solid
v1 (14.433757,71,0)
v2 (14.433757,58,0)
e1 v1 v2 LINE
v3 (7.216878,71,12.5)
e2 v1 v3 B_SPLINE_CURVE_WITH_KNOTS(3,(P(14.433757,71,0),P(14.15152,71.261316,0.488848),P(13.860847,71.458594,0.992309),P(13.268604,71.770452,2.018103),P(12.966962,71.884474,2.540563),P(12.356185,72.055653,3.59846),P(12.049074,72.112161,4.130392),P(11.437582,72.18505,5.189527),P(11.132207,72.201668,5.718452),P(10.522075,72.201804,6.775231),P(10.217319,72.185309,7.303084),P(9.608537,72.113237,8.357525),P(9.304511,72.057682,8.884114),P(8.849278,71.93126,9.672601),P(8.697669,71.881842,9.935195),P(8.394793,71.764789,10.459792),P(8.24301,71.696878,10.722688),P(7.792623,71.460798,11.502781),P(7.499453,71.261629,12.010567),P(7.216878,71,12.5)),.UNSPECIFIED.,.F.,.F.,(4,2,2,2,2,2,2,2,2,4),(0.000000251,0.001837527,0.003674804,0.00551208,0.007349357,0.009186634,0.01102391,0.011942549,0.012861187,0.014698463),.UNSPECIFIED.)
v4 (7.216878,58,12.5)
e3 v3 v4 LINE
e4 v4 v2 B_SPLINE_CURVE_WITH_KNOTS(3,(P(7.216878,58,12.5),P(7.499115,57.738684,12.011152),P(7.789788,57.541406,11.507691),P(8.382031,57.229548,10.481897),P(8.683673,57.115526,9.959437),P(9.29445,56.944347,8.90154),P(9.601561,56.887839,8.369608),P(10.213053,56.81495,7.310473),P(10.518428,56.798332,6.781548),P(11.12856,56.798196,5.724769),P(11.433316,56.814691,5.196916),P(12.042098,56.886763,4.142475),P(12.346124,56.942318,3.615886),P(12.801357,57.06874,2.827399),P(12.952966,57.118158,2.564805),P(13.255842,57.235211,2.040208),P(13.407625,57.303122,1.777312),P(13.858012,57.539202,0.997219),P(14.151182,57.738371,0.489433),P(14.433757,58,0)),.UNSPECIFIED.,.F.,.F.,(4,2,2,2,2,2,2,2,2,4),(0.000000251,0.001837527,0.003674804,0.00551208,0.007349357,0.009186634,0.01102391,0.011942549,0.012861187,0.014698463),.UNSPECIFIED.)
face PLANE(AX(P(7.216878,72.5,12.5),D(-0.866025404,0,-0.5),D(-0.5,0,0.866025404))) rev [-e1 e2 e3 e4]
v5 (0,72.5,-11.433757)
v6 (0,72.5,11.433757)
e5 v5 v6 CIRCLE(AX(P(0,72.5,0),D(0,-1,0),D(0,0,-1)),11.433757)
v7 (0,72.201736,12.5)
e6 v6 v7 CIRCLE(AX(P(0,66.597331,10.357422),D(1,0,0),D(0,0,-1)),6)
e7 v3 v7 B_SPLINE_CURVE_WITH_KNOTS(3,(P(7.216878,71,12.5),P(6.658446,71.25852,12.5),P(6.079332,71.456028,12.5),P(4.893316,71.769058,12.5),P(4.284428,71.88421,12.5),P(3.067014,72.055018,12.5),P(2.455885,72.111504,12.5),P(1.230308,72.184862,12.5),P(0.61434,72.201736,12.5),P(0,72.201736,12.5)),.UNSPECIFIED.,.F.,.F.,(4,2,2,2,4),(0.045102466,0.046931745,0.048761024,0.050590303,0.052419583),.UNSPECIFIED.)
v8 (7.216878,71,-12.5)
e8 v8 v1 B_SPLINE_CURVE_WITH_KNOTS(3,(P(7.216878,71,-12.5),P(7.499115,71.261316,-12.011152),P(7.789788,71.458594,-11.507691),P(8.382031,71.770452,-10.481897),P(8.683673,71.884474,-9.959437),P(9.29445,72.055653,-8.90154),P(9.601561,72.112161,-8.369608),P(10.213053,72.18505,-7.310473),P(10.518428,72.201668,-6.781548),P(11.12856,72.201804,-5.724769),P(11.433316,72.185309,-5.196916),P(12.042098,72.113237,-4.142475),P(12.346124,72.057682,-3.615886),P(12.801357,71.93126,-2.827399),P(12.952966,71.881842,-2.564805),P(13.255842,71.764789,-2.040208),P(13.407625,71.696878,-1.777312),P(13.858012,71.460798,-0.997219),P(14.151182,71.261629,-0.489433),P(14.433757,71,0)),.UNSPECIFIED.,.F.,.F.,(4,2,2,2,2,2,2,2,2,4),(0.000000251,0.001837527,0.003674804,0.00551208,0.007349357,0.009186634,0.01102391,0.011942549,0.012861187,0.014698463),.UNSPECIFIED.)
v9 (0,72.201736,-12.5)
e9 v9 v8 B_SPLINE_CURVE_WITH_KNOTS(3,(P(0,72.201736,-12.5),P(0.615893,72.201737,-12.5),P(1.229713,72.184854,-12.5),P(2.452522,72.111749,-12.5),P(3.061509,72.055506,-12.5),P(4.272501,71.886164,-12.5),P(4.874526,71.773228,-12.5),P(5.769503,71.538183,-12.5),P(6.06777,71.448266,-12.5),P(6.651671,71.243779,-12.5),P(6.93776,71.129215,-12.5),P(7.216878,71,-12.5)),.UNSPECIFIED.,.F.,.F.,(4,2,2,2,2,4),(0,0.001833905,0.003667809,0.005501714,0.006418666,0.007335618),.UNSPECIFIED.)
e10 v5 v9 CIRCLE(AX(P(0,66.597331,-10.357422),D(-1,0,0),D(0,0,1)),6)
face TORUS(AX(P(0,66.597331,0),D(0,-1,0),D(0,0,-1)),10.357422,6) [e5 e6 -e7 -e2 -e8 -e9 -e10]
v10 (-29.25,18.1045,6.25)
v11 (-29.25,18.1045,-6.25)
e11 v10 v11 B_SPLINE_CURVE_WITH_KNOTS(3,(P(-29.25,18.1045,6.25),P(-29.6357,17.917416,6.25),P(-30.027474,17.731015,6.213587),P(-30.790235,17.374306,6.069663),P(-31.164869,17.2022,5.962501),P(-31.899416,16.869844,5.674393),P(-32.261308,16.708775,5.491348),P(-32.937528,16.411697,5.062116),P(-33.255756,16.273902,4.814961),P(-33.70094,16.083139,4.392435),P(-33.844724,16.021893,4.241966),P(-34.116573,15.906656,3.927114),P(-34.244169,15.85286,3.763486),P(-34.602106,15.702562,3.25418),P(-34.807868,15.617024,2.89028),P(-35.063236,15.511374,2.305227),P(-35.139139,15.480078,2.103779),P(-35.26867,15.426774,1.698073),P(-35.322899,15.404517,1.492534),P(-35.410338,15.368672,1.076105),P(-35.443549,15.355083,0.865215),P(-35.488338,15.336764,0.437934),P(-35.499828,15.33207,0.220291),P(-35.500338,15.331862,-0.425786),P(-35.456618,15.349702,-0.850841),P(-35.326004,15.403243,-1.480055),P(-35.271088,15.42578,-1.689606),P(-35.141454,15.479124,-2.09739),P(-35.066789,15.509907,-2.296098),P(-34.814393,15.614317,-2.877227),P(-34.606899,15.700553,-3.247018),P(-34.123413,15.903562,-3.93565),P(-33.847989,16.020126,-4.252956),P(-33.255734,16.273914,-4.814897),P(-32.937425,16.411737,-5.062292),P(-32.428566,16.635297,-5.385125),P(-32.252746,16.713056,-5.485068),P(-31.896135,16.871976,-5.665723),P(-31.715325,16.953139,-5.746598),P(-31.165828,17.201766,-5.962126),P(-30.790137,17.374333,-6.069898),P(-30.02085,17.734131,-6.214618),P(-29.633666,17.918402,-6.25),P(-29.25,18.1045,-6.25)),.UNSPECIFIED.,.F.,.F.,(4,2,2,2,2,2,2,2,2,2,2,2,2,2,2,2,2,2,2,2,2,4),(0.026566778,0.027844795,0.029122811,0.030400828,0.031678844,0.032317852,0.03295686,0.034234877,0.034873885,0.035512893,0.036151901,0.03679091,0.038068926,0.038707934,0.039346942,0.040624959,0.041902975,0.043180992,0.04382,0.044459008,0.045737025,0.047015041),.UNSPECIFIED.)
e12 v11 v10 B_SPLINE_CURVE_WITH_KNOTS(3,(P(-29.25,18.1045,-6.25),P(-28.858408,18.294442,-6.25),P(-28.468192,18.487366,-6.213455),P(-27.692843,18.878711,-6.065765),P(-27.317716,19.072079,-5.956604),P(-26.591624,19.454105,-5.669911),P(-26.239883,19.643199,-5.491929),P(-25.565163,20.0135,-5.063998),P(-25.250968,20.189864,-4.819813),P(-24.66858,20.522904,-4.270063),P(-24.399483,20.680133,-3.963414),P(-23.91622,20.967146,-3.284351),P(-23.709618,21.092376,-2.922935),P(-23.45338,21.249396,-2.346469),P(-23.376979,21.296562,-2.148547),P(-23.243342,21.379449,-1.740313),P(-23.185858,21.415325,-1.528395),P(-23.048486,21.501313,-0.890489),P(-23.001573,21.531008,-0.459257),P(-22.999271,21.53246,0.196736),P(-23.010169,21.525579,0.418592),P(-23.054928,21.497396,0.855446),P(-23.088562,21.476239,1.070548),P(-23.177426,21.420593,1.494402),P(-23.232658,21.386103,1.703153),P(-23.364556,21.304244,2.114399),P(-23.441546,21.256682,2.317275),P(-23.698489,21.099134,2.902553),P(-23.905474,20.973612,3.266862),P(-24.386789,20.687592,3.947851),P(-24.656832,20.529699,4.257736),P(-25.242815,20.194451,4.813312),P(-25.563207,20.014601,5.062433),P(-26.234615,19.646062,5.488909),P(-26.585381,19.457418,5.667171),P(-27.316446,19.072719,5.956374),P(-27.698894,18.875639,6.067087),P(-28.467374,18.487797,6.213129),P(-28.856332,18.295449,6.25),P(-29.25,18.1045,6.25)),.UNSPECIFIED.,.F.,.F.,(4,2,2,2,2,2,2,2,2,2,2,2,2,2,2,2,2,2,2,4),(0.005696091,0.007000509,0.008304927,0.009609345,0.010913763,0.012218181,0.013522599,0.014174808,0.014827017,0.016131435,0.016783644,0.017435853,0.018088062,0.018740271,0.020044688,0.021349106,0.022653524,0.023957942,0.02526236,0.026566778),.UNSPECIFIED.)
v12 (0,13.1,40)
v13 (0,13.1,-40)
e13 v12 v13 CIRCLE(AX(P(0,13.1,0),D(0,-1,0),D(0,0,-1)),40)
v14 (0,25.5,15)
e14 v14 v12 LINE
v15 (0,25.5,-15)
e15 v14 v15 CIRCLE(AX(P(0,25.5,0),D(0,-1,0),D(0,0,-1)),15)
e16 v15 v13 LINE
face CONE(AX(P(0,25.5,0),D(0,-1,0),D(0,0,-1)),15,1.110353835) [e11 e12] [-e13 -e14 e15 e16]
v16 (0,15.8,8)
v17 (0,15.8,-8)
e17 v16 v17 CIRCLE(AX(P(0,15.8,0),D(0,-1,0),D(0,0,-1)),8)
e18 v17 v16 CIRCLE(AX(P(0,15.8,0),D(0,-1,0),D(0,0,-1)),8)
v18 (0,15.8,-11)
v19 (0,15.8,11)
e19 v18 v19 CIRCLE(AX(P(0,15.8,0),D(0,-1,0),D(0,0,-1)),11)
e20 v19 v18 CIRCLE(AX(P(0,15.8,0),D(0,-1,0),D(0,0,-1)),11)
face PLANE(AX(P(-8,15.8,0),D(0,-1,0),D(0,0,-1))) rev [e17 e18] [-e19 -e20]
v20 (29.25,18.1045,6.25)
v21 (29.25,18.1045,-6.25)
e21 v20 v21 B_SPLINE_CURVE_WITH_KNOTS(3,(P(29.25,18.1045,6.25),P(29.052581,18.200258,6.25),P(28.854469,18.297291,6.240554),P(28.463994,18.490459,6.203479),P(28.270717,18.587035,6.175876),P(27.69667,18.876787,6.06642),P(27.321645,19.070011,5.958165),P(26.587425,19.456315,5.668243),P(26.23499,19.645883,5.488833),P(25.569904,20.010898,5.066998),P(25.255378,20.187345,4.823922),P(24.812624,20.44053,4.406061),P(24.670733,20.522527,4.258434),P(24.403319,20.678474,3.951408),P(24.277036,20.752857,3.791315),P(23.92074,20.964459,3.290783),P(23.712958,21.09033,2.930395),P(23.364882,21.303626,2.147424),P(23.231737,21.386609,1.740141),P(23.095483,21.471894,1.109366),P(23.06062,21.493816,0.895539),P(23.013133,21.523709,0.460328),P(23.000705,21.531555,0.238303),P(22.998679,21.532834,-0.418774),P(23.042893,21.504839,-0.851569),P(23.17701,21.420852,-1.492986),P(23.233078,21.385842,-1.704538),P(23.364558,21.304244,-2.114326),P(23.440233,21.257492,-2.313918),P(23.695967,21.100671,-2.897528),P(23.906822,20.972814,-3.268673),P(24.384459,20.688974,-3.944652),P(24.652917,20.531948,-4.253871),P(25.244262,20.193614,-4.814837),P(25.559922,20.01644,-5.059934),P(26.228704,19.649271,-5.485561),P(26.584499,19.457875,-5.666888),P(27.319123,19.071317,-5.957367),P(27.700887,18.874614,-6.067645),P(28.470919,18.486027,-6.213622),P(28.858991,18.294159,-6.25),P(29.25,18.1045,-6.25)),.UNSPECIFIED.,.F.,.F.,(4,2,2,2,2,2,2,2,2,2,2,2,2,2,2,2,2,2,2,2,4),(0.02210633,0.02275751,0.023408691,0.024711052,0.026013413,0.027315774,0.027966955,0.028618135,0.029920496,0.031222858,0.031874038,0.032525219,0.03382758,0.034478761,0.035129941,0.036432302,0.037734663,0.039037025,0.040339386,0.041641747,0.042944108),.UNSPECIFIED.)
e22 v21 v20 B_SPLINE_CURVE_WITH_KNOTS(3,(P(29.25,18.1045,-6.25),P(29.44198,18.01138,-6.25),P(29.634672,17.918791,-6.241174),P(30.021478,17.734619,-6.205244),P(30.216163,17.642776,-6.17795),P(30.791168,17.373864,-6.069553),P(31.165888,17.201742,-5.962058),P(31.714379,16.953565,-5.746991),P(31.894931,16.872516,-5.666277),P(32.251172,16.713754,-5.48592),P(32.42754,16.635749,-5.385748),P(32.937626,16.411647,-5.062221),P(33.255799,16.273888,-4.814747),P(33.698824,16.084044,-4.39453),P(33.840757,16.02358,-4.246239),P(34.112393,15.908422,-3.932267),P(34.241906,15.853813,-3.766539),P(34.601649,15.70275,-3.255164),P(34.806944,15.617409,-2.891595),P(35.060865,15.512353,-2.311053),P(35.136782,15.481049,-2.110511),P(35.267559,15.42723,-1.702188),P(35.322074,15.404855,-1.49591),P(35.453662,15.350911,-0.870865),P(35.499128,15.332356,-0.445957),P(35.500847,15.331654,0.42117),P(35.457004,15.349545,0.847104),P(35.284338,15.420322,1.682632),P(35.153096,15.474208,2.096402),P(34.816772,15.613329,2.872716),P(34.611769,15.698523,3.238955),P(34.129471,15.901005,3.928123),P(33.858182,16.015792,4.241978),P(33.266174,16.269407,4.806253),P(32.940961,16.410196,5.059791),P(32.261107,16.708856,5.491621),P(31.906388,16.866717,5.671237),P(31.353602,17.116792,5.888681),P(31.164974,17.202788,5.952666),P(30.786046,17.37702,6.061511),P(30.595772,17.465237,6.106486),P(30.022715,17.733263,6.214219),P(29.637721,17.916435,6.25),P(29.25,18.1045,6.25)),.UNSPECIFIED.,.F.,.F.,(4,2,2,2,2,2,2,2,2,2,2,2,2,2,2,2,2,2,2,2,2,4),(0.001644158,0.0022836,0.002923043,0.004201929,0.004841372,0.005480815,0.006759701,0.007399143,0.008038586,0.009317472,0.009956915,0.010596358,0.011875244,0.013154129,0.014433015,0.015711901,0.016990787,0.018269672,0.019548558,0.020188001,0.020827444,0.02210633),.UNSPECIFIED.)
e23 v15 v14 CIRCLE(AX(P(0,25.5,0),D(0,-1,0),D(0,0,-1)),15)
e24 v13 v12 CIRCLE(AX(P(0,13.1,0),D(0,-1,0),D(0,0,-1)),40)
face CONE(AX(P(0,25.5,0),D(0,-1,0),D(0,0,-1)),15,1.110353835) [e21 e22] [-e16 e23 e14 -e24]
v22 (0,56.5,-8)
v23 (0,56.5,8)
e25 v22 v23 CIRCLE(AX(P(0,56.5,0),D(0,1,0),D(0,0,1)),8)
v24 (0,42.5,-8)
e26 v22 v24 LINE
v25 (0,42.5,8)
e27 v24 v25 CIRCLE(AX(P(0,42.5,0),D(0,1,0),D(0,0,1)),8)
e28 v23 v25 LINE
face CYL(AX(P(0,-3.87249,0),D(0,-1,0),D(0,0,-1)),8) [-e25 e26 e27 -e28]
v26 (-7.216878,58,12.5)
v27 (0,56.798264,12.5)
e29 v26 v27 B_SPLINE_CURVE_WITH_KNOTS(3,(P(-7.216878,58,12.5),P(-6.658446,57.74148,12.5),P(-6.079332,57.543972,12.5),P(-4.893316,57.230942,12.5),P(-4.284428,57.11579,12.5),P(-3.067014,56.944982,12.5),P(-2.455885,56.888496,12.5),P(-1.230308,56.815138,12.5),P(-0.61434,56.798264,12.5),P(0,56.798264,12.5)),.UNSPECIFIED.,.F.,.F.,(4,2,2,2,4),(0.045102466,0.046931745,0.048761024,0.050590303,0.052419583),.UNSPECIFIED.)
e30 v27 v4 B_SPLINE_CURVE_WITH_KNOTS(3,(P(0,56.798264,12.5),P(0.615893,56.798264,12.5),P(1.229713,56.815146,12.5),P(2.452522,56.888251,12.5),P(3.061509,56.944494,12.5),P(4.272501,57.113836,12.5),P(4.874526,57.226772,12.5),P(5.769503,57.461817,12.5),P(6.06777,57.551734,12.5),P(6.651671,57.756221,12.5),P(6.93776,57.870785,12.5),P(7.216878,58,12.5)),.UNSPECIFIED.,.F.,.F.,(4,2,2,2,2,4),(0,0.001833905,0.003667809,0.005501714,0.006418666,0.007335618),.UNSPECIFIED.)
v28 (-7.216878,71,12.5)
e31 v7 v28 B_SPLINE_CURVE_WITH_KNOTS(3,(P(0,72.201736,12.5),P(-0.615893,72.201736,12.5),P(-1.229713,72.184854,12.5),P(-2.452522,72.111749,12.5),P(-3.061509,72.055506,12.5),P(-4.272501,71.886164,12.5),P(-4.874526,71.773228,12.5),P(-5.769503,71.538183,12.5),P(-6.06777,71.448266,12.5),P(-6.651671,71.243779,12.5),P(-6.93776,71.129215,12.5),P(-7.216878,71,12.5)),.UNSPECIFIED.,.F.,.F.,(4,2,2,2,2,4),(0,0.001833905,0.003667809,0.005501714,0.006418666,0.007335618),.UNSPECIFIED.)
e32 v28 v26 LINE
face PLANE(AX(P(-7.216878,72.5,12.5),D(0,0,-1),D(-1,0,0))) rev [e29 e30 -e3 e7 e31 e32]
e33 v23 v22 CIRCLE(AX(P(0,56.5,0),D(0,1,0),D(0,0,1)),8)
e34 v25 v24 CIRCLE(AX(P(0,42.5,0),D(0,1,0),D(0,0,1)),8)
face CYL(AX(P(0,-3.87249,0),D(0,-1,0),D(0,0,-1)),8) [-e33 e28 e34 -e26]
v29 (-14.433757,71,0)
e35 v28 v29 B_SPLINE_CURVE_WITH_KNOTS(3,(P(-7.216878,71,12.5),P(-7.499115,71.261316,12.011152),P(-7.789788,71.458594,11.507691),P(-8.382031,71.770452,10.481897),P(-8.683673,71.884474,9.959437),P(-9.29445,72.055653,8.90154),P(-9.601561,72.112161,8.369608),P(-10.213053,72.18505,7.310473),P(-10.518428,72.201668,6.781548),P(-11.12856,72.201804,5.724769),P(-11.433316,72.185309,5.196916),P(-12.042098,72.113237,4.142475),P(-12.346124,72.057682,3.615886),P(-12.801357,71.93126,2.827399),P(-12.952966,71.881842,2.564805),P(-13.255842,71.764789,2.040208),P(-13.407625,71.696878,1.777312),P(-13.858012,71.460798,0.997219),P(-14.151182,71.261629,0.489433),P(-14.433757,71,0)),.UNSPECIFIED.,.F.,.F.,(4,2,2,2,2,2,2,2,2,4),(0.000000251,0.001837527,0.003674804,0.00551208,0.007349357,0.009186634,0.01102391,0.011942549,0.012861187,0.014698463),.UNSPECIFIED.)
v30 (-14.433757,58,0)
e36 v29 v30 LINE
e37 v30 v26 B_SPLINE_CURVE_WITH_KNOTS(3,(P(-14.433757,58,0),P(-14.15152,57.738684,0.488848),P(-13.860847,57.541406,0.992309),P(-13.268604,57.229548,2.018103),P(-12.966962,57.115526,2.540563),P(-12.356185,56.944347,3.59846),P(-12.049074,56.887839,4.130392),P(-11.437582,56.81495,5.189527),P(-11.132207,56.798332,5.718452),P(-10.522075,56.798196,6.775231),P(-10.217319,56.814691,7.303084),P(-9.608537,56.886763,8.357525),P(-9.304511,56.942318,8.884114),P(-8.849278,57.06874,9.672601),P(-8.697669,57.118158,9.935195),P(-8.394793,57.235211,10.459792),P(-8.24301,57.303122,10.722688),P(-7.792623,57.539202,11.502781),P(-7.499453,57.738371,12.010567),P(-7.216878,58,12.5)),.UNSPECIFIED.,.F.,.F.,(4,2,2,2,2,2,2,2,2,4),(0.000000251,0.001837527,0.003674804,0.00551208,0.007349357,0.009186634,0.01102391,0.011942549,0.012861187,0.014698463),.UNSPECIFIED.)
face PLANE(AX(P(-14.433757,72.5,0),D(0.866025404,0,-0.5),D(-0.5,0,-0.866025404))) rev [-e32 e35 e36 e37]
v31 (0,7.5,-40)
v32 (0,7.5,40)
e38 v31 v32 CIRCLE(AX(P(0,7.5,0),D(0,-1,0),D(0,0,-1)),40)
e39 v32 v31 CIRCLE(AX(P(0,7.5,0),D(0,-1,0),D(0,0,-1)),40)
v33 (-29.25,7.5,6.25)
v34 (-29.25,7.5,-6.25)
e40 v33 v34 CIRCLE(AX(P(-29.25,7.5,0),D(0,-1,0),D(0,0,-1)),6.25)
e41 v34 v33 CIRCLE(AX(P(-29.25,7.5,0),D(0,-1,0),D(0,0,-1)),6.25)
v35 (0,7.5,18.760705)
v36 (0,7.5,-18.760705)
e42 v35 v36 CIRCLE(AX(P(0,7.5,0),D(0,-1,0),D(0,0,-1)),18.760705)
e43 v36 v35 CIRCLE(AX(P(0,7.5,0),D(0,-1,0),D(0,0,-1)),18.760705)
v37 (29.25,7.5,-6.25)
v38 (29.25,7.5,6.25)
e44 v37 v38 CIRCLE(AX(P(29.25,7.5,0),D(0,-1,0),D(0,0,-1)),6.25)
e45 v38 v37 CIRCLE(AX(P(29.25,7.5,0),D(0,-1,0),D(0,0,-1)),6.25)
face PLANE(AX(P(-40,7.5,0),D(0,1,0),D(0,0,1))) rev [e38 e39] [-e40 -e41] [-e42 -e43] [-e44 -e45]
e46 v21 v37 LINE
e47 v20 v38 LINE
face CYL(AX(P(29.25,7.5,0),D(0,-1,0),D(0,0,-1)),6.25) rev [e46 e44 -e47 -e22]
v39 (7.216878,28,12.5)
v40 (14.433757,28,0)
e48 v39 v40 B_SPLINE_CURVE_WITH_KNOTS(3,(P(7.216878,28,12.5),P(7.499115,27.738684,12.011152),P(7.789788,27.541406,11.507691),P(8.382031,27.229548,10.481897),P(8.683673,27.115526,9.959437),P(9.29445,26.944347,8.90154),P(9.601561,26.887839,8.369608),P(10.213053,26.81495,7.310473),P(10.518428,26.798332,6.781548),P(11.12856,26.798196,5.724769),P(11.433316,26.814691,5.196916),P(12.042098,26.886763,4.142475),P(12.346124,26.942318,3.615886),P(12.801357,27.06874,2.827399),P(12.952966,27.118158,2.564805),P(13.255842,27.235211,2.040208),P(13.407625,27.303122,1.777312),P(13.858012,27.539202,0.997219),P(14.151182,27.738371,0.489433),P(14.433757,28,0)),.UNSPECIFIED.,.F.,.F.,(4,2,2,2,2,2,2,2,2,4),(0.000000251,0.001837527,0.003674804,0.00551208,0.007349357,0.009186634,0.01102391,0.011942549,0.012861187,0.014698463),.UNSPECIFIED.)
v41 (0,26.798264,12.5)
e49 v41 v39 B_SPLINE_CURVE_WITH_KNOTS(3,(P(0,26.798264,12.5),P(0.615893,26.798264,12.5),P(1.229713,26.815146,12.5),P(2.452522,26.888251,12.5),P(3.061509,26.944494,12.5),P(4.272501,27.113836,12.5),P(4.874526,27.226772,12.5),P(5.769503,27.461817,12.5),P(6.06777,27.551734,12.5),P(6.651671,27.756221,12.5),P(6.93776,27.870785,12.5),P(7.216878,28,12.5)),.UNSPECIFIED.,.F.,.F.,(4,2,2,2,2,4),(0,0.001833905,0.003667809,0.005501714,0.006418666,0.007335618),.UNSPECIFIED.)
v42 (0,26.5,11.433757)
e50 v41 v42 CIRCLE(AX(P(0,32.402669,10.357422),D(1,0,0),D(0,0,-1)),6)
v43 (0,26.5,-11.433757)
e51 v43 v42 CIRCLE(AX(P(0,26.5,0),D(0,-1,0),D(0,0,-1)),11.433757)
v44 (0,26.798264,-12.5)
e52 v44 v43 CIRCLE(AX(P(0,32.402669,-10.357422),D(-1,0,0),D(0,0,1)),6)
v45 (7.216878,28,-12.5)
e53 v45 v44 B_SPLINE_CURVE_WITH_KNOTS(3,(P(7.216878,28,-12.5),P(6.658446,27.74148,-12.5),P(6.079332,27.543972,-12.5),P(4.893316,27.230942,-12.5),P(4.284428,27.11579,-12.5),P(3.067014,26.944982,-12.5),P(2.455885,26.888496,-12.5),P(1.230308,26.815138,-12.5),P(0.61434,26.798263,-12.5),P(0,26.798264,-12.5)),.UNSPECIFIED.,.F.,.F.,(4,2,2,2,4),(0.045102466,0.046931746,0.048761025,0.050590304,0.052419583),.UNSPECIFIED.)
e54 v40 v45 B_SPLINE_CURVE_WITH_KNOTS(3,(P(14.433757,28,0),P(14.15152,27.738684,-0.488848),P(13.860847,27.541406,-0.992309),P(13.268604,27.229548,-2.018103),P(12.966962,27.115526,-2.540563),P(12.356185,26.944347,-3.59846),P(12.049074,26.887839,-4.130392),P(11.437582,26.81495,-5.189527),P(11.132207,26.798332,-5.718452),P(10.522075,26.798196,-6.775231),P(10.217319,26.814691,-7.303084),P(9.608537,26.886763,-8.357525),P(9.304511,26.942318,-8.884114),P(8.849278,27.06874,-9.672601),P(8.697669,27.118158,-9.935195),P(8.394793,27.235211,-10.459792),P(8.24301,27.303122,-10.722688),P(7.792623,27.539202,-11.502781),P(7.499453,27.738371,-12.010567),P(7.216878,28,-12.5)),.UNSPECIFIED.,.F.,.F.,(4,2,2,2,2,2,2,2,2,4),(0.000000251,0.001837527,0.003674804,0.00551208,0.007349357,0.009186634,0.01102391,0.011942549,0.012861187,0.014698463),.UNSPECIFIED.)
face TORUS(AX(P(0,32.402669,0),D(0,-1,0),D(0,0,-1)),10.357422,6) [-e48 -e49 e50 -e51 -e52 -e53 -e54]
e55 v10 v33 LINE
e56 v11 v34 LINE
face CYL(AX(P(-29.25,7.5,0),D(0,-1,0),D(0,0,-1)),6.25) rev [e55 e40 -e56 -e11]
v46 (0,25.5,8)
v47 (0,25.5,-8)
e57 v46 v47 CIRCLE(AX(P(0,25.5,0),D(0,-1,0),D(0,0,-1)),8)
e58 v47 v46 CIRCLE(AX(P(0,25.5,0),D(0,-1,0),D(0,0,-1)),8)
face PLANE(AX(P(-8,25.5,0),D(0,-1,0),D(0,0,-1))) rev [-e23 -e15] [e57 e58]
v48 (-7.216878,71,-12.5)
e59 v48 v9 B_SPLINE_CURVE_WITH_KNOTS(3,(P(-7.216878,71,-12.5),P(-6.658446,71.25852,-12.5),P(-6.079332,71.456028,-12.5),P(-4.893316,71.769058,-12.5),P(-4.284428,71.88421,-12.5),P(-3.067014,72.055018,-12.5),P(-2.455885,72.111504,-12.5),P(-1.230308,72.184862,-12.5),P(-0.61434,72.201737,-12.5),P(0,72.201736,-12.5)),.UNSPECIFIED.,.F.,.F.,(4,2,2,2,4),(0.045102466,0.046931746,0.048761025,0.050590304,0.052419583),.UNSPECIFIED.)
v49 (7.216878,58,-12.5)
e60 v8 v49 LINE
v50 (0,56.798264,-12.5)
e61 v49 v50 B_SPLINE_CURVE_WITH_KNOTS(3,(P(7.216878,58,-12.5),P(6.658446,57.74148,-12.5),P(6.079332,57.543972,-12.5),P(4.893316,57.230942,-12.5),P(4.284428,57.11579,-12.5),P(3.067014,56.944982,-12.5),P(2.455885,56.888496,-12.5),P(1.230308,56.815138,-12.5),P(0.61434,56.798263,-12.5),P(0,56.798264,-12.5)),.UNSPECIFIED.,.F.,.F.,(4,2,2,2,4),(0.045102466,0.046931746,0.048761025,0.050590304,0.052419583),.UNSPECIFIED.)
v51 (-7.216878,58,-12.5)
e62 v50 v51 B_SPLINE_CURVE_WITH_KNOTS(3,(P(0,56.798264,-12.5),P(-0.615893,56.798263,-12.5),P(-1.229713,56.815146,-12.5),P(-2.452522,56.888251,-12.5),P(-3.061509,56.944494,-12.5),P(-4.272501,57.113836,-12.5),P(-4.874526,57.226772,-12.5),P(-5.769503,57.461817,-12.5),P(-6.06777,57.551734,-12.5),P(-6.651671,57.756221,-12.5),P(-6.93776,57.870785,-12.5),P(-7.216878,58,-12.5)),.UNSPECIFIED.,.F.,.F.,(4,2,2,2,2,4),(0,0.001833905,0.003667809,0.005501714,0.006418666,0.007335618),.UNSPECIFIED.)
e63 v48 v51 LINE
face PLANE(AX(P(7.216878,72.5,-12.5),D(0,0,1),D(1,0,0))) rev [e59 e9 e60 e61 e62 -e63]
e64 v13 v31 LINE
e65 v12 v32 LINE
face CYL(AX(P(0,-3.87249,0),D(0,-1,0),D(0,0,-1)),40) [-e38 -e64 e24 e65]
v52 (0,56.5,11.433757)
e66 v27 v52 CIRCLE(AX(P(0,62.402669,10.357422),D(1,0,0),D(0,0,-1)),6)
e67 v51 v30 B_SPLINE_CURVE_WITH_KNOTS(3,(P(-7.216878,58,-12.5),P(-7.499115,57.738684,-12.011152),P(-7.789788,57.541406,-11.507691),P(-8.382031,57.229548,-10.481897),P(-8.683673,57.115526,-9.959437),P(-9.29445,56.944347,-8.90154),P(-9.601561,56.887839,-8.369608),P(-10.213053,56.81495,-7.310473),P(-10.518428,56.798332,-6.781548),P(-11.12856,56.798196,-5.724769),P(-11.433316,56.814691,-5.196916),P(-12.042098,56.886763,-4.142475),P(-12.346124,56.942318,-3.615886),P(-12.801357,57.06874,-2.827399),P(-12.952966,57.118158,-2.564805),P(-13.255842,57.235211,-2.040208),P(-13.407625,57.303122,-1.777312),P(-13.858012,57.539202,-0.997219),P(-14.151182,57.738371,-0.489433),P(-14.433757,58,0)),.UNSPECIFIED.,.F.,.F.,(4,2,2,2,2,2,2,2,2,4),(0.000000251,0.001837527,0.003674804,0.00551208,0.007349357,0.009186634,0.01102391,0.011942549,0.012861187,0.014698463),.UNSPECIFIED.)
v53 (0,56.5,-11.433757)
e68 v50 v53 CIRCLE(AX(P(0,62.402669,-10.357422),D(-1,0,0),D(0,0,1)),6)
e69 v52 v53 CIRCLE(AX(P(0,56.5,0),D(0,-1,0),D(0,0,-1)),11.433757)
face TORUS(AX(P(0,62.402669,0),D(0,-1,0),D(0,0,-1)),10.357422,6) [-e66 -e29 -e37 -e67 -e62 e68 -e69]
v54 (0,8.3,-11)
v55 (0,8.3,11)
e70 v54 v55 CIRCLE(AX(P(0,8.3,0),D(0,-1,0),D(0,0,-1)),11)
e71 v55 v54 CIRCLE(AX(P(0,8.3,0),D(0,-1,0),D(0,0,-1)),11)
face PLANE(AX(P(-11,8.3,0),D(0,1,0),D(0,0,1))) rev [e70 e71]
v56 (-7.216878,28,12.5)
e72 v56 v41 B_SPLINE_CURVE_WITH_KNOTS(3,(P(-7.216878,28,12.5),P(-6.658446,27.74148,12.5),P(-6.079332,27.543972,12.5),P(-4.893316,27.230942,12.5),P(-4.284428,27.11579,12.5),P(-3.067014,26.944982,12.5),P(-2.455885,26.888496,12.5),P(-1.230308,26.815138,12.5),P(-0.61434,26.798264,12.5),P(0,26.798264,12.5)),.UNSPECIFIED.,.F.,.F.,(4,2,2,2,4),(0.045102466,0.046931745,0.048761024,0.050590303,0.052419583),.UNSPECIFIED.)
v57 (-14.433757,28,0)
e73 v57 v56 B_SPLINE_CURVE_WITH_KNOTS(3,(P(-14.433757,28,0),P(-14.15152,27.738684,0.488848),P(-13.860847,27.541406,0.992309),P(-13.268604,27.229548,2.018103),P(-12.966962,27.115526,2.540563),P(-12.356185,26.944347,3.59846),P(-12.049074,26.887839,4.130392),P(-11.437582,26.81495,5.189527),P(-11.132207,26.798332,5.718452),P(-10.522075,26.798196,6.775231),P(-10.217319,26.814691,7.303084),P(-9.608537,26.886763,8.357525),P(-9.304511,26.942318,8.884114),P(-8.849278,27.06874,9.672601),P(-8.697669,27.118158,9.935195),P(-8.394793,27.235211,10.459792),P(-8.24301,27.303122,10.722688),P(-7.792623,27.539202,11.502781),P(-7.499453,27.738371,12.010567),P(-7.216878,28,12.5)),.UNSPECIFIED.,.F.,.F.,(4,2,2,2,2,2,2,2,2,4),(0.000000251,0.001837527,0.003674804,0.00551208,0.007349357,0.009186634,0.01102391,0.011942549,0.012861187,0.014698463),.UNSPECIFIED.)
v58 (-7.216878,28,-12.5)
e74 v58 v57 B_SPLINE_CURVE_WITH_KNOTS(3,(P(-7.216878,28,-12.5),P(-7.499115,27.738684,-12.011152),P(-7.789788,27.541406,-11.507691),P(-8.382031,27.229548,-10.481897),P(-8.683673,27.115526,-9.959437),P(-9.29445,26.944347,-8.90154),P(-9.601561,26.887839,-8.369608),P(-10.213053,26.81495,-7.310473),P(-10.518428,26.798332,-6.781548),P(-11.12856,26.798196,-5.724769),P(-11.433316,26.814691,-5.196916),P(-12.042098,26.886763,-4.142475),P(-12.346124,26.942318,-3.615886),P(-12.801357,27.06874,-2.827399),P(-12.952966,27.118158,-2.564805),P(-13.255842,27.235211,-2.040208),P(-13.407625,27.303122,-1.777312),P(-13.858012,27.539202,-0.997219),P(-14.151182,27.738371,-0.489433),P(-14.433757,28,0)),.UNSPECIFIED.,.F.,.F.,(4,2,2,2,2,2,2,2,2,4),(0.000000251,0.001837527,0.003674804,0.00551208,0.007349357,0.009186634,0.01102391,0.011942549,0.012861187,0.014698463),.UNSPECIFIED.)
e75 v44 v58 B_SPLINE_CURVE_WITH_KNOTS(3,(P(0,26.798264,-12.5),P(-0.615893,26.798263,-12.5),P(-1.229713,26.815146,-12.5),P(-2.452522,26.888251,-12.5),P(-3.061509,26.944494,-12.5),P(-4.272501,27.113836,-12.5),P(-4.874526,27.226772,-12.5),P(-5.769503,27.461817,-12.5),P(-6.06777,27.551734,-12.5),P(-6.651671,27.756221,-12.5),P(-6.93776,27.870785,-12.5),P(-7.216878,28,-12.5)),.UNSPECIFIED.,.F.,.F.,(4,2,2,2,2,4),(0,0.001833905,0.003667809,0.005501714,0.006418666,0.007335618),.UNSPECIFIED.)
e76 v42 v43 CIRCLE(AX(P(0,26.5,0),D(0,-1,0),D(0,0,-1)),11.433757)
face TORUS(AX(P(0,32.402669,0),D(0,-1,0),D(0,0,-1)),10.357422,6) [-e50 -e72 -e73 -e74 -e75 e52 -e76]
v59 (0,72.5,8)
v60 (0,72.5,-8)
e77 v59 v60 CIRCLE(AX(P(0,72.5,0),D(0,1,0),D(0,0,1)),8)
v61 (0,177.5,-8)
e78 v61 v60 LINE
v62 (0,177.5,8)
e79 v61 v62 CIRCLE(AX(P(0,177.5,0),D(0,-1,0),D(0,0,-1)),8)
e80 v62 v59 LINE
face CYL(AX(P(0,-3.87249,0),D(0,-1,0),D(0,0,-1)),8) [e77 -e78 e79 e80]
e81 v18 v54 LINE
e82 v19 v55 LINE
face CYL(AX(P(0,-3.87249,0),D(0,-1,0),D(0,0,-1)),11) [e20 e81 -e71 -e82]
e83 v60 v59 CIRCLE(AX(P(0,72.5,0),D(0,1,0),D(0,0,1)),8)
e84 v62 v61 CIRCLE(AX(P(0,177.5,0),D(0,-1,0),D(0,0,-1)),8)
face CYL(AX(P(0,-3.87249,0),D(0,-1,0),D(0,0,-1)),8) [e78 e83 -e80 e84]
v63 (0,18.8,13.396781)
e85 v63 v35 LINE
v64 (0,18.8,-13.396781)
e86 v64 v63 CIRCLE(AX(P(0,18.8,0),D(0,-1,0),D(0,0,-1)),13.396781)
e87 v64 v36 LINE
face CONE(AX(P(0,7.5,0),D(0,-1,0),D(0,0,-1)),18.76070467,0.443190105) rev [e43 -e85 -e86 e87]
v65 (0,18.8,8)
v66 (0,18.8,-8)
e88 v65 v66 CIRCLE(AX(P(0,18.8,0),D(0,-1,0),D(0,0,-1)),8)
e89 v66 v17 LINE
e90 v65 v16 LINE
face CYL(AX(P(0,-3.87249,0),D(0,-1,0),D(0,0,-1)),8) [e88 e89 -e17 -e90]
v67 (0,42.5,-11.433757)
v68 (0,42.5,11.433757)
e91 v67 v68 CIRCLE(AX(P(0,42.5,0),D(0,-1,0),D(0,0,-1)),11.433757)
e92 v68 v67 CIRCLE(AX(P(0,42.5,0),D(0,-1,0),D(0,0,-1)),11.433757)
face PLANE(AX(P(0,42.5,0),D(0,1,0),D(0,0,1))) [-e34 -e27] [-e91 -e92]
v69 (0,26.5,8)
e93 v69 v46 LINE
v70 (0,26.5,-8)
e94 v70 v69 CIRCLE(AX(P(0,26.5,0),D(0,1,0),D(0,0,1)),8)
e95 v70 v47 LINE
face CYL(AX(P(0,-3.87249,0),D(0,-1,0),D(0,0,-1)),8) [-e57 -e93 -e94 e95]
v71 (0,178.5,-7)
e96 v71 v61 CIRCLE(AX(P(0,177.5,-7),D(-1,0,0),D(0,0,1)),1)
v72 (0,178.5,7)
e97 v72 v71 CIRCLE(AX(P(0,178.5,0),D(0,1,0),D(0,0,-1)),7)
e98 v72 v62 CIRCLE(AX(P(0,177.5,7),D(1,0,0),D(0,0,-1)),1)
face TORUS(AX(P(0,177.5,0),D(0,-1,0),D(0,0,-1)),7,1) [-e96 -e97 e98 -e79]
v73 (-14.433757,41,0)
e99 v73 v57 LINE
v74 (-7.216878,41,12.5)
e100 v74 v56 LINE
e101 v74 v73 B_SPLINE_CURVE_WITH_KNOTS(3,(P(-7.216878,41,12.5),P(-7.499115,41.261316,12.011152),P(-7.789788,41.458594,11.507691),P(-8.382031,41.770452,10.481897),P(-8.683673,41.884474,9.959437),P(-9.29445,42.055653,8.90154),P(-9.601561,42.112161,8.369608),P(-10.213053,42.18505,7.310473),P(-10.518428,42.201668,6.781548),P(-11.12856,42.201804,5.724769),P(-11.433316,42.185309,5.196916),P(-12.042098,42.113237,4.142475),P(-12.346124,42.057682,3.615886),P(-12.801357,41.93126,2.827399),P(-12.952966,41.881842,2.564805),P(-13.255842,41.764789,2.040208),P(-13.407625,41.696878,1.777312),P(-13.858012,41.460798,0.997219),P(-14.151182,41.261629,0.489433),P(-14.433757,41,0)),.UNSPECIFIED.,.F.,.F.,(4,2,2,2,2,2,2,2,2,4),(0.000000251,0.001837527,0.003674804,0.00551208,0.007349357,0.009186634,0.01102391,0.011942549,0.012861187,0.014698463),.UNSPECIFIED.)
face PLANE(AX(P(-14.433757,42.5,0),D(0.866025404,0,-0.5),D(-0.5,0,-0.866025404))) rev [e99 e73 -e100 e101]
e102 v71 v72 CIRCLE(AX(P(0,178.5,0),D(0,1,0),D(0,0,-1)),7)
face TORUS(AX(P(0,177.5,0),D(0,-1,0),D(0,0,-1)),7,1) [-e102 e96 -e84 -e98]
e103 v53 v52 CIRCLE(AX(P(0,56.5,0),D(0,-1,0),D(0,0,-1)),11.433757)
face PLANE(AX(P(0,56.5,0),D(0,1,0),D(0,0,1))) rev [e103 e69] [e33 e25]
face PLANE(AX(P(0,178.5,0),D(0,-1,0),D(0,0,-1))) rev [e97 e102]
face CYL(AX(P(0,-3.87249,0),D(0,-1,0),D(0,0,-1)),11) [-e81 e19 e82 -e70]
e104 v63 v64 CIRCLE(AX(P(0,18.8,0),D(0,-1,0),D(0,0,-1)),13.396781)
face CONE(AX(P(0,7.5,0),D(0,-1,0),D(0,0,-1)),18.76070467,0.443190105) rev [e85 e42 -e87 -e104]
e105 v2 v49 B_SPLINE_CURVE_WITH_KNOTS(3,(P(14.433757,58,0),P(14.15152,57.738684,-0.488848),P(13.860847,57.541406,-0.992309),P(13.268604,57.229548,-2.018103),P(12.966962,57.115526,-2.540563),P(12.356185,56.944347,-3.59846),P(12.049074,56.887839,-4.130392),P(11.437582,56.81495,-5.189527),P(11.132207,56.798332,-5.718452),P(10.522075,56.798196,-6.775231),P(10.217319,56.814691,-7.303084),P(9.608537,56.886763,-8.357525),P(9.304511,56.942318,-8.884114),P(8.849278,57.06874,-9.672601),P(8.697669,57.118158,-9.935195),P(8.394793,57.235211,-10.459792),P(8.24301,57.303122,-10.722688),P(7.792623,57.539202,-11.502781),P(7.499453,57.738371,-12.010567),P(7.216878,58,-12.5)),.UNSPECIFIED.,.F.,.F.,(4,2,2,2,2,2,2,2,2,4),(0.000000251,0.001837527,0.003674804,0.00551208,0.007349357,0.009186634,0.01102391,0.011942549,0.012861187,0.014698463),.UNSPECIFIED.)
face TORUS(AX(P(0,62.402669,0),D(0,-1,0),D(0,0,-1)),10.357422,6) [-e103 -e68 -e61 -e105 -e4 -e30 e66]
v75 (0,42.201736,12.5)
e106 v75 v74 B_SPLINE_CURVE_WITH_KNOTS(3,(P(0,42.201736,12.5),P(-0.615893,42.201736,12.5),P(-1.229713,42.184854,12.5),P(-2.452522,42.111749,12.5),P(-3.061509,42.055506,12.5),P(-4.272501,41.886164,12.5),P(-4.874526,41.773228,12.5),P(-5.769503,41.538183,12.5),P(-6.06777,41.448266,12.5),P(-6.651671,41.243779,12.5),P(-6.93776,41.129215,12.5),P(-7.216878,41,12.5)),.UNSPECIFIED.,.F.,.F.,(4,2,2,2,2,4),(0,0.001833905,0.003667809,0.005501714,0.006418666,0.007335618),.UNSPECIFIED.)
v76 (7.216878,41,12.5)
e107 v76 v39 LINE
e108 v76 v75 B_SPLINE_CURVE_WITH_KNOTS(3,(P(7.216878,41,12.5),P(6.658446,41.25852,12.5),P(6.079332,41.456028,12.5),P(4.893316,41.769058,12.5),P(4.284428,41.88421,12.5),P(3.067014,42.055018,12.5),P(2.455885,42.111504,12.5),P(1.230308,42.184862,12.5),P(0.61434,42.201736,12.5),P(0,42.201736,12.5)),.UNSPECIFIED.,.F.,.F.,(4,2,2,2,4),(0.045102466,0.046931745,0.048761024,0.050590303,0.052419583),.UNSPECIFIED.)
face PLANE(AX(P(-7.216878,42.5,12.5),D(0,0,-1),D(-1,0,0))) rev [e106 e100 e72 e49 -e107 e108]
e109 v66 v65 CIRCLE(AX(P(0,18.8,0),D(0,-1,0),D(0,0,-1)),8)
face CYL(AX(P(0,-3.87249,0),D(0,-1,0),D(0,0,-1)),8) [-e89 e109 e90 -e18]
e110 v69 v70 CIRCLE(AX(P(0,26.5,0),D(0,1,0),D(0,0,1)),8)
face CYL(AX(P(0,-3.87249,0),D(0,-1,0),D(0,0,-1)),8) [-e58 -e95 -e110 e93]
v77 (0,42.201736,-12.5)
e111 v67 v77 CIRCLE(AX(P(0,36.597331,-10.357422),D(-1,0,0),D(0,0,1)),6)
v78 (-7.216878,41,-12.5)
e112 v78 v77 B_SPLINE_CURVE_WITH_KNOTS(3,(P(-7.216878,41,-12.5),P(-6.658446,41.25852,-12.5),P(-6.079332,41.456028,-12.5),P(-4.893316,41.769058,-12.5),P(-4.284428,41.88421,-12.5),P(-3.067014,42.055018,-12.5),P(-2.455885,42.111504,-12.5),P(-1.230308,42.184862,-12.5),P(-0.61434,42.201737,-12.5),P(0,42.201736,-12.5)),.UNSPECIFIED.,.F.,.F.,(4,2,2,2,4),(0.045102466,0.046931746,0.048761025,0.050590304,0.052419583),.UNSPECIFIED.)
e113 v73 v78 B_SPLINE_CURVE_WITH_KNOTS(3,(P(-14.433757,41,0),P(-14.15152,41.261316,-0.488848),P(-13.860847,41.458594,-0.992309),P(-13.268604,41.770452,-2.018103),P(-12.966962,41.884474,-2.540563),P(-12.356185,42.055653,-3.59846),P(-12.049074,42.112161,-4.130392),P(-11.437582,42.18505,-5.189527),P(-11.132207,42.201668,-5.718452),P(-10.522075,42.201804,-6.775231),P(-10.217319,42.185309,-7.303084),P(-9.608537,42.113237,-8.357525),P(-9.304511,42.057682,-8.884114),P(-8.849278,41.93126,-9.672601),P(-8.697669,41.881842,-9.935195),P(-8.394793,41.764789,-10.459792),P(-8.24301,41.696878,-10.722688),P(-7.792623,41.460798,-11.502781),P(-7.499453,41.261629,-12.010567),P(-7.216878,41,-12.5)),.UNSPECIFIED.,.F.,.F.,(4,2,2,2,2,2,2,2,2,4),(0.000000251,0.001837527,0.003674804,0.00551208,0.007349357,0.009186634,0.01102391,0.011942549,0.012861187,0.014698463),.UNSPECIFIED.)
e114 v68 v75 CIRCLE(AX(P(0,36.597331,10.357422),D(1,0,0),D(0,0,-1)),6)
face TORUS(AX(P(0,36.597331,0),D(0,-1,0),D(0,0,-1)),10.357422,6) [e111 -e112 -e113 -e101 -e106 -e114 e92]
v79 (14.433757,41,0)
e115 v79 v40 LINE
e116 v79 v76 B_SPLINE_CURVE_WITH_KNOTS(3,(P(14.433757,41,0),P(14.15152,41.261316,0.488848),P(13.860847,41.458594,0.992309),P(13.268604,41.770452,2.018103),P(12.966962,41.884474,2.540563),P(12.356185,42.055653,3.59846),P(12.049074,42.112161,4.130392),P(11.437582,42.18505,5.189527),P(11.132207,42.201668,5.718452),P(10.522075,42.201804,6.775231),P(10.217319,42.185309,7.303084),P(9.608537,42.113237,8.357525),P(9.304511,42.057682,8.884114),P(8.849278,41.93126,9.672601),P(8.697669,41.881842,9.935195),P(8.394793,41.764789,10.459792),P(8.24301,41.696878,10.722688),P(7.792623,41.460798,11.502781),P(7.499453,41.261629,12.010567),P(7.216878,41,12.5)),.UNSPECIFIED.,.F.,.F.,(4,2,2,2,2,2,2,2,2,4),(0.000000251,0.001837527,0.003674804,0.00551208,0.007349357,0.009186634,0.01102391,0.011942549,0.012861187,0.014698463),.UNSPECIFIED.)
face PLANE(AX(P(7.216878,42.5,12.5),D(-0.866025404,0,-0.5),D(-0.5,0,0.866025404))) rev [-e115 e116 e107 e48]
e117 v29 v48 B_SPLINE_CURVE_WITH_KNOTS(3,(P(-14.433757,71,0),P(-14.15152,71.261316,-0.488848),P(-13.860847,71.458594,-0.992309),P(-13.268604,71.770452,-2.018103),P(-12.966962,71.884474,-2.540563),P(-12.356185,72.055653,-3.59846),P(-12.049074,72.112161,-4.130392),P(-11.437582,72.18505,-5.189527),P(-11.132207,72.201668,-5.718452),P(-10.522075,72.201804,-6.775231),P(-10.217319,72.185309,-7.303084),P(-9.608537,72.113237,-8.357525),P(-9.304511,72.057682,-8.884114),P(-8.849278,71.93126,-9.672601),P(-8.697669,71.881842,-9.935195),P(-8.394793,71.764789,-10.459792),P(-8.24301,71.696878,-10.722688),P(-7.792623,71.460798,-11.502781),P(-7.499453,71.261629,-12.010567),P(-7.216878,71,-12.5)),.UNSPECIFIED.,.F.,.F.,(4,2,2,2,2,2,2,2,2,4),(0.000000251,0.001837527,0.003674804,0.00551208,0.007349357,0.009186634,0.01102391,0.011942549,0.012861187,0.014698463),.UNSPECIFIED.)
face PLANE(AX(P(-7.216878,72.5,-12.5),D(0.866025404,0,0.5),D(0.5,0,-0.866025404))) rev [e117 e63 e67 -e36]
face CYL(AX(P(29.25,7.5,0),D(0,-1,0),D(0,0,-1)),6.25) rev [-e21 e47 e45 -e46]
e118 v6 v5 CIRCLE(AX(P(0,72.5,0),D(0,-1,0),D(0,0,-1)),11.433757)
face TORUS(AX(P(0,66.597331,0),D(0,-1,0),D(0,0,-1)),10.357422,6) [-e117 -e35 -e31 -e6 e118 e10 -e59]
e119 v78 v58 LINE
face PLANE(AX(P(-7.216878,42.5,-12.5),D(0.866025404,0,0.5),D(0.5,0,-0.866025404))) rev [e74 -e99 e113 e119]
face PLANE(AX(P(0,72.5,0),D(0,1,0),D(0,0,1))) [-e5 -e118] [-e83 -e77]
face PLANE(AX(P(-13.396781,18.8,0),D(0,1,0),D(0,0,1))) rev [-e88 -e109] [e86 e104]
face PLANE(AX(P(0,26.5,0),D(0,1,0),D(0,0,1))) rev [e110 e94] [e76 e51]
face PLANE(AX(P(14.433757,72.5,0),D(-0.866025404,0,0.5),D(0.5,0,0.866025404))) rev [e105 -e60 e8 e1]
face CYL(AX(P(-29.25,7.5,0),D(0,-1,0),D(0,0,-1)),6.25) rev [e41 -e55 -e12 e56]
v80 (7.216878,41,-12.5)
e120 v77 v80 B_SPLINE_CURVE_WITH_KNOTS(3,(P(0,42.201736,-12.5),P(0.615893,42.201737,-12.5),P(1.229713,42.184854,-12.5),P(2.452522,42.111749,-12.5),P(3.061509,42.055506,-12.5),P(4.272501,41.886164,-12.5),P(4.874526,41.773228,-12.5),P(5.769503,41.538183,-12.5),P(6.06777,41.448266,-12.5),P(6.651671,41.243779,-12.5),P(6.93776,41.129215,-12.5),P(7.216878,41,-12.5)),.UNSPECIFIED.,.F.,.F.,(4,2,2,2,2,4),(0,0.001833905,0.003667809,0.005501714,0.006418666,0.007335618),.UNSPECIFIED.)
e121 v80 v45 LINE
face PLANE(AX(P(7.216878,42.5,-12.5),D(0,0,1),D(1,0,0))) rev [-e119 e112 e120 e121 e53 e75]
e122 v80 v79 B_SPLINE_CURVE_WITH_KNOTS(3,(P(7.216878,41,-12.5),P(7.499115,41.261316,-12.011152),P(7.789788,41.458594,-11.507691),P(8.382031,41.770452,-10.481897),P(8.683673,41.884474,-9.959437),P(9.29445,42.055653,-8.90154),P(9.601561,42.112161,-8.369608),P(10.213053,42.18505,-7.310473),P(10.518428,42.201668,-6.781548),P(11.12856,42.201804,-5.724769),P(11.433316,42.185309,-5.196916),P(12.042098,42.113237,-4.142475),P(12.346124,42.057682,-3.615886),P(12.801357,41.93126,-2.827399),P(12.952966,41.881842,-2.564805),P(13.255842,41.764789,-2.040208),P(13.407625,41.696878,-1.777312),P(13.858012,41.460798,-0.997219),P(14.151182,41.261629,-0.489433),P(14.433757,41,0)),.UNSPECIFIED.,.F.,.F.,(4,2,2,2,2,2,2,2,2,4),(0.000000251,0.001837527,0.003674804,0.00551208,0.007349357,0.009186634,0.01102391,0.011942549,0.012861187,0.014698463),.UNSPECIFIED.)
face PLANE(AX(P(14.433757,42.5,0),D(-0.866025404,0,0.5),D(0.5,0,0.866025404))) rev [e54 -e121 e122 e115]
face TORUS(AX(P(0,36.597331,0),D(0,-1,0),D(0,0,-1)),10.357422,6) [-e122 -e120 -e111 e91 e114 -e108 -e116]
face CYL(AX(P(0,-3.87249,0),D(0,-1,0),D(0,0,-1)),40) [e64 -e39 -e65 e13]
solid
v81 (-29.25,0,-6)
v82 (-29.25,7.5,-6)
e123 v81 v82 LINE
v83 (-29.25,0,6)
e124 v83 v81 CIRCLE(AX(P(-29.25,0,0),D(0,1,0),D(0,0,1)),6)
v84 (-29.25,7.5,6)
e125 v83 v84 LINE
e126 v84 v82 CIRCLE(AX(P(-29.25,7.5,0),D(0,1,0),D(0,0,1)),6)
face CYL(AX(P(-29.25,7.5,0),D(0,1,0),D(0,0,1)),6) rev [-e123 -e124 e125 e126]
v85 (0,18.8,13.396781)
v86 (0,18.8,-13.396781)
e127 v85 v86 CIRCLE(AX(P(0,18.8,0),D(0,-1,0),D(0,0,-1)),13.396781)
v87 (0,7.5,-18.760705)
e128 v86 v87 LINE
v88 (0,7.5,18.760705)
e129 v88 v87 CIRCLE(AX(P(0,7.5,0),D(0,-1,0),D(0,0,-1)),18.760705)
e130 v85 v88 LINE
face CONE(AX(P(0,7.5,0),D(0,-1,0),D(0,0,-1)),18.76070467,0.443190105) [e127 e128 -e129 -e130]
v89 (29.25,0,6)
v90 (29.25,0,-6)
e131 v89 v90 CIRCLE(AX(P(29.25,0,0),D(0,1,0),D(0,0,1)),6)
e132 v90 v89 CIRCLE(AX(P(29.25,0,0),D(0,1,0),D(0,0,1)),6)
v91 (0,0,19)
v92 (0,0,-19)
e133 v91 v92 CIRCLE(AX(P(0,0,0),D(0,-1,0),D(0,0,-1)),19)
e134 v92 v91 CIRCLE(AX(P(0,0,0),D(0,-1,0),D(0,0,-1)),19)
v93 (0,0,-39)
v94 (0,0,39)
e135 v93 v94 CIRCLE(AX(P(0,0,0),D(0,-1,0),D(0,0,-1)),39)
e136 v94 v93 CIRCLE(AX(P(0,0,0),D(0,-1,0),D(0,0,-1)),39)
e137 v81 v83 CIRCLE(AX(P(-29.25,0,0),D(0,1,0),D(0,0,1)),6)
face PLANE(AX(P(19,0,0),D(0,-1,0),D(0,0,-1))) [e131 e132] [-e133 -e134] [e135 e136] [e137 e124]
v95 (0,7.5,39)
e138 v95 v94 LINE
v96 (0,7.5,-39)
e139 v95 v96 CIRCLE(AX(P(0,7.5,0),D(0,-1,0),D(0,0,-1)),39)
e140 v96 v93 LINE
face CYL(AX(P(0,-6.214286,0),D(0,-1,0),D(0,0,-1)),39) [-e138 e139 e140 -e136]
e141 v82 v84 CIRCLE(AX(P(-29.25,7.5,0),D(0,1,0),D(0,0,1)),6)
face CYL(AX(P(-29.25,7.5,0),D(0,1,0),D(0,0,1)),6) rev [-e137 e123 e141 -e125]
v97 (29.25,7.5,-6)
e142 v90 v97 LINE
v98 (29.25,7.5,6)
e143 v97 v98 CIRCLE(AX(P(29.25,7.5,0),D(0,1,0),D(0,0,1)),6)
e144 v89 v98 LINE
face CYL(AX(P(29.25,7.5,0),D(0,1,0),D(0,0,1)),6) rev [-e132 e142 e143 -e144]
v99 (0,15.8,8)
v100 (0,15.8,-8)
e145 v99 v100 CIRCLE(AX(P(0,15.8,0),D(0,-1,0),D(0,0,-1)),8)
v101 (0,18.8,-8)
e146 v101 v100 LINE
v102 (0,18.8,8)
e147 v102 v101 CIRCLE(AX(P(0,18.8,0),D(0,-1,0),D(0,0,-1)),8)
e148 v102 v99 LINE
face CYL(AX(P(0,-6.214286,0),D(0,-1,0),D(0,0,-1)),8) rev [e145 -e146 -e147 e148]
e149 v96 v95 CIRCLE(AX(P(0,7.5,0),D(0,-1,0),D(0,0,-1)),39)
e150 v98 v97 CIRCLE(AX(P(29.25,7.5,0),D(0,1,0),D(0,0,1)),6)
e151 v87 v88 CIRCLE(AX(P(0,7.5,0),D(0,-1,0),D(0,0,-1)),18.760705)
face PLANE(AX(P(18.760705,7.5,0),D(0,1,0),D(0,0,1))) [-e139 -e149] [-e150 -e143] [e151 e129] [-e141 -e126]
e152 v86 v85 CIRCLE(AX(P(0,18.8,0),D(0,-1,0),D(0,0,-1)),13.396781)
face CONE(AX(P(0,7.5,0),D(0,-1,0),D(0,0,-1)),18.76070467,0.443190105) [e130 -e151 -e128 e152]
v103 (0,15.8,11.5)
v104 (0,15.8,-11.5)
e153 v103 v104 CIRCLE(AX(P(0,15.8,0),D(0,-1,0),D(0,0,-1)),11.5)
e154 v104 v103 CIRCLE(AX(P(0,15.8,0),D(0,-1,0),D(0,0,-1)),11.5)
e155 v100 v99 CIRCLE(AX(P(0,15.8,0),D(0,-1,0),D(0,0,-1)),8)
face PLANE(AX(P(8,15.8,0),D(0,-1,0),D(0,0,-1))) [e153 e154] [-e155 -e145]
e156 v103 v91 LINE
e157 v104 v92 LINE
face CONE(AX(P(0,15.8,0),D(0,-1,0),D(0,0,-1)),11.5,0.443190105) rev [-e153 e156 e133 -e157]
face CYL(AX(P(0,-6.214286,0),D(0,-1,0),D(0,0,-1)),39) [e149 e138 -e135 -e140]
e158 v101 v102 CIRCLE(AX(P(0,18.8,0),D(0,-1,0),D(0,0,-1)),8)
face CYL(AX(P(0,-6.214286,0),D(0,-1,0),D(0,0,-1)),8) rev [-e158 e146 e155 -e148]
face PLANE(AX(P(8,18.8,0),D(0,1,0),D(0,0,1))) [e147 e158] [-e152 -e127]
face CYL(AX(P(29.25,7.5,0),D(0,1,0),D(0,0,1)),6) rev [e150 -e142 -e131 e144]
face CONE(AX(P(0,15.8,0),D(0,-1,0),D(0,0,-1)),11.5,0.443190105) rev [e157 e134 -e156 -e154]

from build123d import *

# Parameters (mm, degrees)
HOLE_WIZARD_12_0_12_1_D            = 12
EXTRUDE_1_DEPTH                    = 16
PATTERN_LINEAR_1_COUNT             = 2
PATTERN_LINEAR_1_PITCH             = 30
SKETCH_9_W                         = 6.25
SKETCH_9_H                         = 171
HOLE_WIZARD_12_5_12_5_1_AT_2_COUNT = 2
HOLE_WIZARD_12_5_12_5_1_AT_2_PITCH = 58.5
FILLET_1_R                         = 1


with BuildPart() as part:
    # 草图1 → 旋转1 (revolve)
    with BuildSketch(Plane.XY, mode=Mode.PRIVATE) as revolve_1_sk:
        Polygon((18.76070467, 7.5), (13.396780619, 18.8), (8, 18.8), (8, 15.8), (11.5, 15.8), (19, 0), (39, 0), (39, 7.5), align=None)
    revolve(revolve_1_sk.sketch.rotate(Axis((0, -6.214285714, 0), (0, 1, 0)), 90), axis=Axis((0, -6.214285714, 0), (0, 1, 0)))

    # Ø12.0 (12) 直径孔1 (through all)
    with Locations(Plane(origin=(0, 7.5, 0), x_dir=(1, 0, 0), z_dir=(0, 1, 0))):
        with Locations((-29.25, 0), (29.25, 0)):
            Hole(HOLE_WIZARD_12_0_12_1_D / 2)


with BuildPart() as body_2:
    # 草图2 → 旋转2 (revolve)
    with BuildSketch(Plane.XY, mode=Mode.PRIVATE) as revolve_2_sk:
        Polygon((-40, 7.5), (-18.76070467, 7.5), (-13.396780619, 18.8), (-8, 18.8), (-8, 15.8), (-11, 15.8), (-11, 8.3), (0, 8.3), (0, 178.5), (-8, 178.5), (-8, 25.5), (-15, 25.5), (-40, 13.1), align=None)
    revolve(revolve_2_sk.sketch.rotate(Axis((0, -3.872490415, 0), (0, 1, 0)), 270), axis=Axis((0, -3.872490415, 0), (0, 1, 0)))

    # 草图6 → 凸台-拉伸1 (add)
    with BuildSketch(Plane(origin=(0, 26.5, 0), x_dir=(1, 0, 0), z_dir=(0, 1, 0))):
        Polygon((14.43375673, 0), (7.216878365, 12.5), (-7.216878365, 12.5), (-14.43375673, 0), (-7.216878365, -12.5), (7.216878365, -12.5), align=None)
    extrude_1 = extrude(amount=EXTRUDE_1_DEPTH)

    # 草图7 → 切除-旋转1 (revolve, cut)
    with BuildSketch(Plane.XY, mode=Mode.PRIVATE) as cut_revolve_1_sk:
        with BuildLine():
            Line((14.43375673, 42.5), (11.43375673, 42.5))
            ThreePointArc((11.43375673, 42.5), (13.040703697, 41.963893935), (14.43375673, 41))
            Line((14.43375673, 41), (14.43375673, 42.5))
        make_face()
        with BuildLine():
            Line((14.43375673, 26.5), (14.43375673, 28))
            ThreePointArc((14.43375673, 28), (13.040703697, 27.036106065), (11.43375673, 26.5))
            Line((11.43375673, 26.5), (14.43375673, 26.5))
        make_face()
    cut_revolve_1 = revolve(cut_revolve_1_sk.sketch.rotate(Axis((0, -6.467317027, 0), (0, 1, 0)), 90), axis=Axis((0, -6.467317027, 0), (0, 1, 0)), mode=Mode.SUBTRACT)

    # 阵列(线性)1: 凸台-拉伸1, 切除-旋转1 ×2
    with Locations(*[(0, i * PATTERN_LINEAR_1_PITCH, 0) for i in range(1, PATTERN_LINEAR_1_COUNT)]):
        add(extrude_1)
        add(cut_revolve_1, mode=Mode.SUBTRACT)

    # 草图9 → Ø12.5 (12.5) 直径孔1 (revolve, cut)
    with BuildSketch(Plane(origin=(29.25, 7.5, 0), x_dir=(0, 0, -1), z_dir=(1, 0, 0))):
        with Locations((3.125, 85.5)):
            Rectangle(SKETCH_9_W, SKETCH_9_H)
    hole_wizard_12_5_12_5_1 = revolve(axis=Axis((29.25, 1.15, 0), (0, 1, 0)), mode=Mode.SUBTRACT)

    # Ø12.5 (12.5) 直径孔1 at 2: Ø12.5 (12.5) 直径孔1 ×2
    with Locations(*[(-i * HOLE_WIZARD_12_5_12_5_1_AT_2_PITCH, 0, 0) for i in range(1, HOLE_WIZARD_12_5_12_5_1_AT_2_COUNT)]):
        add(hole_wizard_12_5_12_5_1, mode=Mode.SUBTRACT)

    # 圆角1
    fillet_1_edges = [body_2.edges().sort_by_distance(p)[0] for p in [
        (0, 178.5, 8),
    ]]
    fillet(fillet_1_edges, radius=FILLET_1_R)


solid = Compound([part.part, body_2.part])
